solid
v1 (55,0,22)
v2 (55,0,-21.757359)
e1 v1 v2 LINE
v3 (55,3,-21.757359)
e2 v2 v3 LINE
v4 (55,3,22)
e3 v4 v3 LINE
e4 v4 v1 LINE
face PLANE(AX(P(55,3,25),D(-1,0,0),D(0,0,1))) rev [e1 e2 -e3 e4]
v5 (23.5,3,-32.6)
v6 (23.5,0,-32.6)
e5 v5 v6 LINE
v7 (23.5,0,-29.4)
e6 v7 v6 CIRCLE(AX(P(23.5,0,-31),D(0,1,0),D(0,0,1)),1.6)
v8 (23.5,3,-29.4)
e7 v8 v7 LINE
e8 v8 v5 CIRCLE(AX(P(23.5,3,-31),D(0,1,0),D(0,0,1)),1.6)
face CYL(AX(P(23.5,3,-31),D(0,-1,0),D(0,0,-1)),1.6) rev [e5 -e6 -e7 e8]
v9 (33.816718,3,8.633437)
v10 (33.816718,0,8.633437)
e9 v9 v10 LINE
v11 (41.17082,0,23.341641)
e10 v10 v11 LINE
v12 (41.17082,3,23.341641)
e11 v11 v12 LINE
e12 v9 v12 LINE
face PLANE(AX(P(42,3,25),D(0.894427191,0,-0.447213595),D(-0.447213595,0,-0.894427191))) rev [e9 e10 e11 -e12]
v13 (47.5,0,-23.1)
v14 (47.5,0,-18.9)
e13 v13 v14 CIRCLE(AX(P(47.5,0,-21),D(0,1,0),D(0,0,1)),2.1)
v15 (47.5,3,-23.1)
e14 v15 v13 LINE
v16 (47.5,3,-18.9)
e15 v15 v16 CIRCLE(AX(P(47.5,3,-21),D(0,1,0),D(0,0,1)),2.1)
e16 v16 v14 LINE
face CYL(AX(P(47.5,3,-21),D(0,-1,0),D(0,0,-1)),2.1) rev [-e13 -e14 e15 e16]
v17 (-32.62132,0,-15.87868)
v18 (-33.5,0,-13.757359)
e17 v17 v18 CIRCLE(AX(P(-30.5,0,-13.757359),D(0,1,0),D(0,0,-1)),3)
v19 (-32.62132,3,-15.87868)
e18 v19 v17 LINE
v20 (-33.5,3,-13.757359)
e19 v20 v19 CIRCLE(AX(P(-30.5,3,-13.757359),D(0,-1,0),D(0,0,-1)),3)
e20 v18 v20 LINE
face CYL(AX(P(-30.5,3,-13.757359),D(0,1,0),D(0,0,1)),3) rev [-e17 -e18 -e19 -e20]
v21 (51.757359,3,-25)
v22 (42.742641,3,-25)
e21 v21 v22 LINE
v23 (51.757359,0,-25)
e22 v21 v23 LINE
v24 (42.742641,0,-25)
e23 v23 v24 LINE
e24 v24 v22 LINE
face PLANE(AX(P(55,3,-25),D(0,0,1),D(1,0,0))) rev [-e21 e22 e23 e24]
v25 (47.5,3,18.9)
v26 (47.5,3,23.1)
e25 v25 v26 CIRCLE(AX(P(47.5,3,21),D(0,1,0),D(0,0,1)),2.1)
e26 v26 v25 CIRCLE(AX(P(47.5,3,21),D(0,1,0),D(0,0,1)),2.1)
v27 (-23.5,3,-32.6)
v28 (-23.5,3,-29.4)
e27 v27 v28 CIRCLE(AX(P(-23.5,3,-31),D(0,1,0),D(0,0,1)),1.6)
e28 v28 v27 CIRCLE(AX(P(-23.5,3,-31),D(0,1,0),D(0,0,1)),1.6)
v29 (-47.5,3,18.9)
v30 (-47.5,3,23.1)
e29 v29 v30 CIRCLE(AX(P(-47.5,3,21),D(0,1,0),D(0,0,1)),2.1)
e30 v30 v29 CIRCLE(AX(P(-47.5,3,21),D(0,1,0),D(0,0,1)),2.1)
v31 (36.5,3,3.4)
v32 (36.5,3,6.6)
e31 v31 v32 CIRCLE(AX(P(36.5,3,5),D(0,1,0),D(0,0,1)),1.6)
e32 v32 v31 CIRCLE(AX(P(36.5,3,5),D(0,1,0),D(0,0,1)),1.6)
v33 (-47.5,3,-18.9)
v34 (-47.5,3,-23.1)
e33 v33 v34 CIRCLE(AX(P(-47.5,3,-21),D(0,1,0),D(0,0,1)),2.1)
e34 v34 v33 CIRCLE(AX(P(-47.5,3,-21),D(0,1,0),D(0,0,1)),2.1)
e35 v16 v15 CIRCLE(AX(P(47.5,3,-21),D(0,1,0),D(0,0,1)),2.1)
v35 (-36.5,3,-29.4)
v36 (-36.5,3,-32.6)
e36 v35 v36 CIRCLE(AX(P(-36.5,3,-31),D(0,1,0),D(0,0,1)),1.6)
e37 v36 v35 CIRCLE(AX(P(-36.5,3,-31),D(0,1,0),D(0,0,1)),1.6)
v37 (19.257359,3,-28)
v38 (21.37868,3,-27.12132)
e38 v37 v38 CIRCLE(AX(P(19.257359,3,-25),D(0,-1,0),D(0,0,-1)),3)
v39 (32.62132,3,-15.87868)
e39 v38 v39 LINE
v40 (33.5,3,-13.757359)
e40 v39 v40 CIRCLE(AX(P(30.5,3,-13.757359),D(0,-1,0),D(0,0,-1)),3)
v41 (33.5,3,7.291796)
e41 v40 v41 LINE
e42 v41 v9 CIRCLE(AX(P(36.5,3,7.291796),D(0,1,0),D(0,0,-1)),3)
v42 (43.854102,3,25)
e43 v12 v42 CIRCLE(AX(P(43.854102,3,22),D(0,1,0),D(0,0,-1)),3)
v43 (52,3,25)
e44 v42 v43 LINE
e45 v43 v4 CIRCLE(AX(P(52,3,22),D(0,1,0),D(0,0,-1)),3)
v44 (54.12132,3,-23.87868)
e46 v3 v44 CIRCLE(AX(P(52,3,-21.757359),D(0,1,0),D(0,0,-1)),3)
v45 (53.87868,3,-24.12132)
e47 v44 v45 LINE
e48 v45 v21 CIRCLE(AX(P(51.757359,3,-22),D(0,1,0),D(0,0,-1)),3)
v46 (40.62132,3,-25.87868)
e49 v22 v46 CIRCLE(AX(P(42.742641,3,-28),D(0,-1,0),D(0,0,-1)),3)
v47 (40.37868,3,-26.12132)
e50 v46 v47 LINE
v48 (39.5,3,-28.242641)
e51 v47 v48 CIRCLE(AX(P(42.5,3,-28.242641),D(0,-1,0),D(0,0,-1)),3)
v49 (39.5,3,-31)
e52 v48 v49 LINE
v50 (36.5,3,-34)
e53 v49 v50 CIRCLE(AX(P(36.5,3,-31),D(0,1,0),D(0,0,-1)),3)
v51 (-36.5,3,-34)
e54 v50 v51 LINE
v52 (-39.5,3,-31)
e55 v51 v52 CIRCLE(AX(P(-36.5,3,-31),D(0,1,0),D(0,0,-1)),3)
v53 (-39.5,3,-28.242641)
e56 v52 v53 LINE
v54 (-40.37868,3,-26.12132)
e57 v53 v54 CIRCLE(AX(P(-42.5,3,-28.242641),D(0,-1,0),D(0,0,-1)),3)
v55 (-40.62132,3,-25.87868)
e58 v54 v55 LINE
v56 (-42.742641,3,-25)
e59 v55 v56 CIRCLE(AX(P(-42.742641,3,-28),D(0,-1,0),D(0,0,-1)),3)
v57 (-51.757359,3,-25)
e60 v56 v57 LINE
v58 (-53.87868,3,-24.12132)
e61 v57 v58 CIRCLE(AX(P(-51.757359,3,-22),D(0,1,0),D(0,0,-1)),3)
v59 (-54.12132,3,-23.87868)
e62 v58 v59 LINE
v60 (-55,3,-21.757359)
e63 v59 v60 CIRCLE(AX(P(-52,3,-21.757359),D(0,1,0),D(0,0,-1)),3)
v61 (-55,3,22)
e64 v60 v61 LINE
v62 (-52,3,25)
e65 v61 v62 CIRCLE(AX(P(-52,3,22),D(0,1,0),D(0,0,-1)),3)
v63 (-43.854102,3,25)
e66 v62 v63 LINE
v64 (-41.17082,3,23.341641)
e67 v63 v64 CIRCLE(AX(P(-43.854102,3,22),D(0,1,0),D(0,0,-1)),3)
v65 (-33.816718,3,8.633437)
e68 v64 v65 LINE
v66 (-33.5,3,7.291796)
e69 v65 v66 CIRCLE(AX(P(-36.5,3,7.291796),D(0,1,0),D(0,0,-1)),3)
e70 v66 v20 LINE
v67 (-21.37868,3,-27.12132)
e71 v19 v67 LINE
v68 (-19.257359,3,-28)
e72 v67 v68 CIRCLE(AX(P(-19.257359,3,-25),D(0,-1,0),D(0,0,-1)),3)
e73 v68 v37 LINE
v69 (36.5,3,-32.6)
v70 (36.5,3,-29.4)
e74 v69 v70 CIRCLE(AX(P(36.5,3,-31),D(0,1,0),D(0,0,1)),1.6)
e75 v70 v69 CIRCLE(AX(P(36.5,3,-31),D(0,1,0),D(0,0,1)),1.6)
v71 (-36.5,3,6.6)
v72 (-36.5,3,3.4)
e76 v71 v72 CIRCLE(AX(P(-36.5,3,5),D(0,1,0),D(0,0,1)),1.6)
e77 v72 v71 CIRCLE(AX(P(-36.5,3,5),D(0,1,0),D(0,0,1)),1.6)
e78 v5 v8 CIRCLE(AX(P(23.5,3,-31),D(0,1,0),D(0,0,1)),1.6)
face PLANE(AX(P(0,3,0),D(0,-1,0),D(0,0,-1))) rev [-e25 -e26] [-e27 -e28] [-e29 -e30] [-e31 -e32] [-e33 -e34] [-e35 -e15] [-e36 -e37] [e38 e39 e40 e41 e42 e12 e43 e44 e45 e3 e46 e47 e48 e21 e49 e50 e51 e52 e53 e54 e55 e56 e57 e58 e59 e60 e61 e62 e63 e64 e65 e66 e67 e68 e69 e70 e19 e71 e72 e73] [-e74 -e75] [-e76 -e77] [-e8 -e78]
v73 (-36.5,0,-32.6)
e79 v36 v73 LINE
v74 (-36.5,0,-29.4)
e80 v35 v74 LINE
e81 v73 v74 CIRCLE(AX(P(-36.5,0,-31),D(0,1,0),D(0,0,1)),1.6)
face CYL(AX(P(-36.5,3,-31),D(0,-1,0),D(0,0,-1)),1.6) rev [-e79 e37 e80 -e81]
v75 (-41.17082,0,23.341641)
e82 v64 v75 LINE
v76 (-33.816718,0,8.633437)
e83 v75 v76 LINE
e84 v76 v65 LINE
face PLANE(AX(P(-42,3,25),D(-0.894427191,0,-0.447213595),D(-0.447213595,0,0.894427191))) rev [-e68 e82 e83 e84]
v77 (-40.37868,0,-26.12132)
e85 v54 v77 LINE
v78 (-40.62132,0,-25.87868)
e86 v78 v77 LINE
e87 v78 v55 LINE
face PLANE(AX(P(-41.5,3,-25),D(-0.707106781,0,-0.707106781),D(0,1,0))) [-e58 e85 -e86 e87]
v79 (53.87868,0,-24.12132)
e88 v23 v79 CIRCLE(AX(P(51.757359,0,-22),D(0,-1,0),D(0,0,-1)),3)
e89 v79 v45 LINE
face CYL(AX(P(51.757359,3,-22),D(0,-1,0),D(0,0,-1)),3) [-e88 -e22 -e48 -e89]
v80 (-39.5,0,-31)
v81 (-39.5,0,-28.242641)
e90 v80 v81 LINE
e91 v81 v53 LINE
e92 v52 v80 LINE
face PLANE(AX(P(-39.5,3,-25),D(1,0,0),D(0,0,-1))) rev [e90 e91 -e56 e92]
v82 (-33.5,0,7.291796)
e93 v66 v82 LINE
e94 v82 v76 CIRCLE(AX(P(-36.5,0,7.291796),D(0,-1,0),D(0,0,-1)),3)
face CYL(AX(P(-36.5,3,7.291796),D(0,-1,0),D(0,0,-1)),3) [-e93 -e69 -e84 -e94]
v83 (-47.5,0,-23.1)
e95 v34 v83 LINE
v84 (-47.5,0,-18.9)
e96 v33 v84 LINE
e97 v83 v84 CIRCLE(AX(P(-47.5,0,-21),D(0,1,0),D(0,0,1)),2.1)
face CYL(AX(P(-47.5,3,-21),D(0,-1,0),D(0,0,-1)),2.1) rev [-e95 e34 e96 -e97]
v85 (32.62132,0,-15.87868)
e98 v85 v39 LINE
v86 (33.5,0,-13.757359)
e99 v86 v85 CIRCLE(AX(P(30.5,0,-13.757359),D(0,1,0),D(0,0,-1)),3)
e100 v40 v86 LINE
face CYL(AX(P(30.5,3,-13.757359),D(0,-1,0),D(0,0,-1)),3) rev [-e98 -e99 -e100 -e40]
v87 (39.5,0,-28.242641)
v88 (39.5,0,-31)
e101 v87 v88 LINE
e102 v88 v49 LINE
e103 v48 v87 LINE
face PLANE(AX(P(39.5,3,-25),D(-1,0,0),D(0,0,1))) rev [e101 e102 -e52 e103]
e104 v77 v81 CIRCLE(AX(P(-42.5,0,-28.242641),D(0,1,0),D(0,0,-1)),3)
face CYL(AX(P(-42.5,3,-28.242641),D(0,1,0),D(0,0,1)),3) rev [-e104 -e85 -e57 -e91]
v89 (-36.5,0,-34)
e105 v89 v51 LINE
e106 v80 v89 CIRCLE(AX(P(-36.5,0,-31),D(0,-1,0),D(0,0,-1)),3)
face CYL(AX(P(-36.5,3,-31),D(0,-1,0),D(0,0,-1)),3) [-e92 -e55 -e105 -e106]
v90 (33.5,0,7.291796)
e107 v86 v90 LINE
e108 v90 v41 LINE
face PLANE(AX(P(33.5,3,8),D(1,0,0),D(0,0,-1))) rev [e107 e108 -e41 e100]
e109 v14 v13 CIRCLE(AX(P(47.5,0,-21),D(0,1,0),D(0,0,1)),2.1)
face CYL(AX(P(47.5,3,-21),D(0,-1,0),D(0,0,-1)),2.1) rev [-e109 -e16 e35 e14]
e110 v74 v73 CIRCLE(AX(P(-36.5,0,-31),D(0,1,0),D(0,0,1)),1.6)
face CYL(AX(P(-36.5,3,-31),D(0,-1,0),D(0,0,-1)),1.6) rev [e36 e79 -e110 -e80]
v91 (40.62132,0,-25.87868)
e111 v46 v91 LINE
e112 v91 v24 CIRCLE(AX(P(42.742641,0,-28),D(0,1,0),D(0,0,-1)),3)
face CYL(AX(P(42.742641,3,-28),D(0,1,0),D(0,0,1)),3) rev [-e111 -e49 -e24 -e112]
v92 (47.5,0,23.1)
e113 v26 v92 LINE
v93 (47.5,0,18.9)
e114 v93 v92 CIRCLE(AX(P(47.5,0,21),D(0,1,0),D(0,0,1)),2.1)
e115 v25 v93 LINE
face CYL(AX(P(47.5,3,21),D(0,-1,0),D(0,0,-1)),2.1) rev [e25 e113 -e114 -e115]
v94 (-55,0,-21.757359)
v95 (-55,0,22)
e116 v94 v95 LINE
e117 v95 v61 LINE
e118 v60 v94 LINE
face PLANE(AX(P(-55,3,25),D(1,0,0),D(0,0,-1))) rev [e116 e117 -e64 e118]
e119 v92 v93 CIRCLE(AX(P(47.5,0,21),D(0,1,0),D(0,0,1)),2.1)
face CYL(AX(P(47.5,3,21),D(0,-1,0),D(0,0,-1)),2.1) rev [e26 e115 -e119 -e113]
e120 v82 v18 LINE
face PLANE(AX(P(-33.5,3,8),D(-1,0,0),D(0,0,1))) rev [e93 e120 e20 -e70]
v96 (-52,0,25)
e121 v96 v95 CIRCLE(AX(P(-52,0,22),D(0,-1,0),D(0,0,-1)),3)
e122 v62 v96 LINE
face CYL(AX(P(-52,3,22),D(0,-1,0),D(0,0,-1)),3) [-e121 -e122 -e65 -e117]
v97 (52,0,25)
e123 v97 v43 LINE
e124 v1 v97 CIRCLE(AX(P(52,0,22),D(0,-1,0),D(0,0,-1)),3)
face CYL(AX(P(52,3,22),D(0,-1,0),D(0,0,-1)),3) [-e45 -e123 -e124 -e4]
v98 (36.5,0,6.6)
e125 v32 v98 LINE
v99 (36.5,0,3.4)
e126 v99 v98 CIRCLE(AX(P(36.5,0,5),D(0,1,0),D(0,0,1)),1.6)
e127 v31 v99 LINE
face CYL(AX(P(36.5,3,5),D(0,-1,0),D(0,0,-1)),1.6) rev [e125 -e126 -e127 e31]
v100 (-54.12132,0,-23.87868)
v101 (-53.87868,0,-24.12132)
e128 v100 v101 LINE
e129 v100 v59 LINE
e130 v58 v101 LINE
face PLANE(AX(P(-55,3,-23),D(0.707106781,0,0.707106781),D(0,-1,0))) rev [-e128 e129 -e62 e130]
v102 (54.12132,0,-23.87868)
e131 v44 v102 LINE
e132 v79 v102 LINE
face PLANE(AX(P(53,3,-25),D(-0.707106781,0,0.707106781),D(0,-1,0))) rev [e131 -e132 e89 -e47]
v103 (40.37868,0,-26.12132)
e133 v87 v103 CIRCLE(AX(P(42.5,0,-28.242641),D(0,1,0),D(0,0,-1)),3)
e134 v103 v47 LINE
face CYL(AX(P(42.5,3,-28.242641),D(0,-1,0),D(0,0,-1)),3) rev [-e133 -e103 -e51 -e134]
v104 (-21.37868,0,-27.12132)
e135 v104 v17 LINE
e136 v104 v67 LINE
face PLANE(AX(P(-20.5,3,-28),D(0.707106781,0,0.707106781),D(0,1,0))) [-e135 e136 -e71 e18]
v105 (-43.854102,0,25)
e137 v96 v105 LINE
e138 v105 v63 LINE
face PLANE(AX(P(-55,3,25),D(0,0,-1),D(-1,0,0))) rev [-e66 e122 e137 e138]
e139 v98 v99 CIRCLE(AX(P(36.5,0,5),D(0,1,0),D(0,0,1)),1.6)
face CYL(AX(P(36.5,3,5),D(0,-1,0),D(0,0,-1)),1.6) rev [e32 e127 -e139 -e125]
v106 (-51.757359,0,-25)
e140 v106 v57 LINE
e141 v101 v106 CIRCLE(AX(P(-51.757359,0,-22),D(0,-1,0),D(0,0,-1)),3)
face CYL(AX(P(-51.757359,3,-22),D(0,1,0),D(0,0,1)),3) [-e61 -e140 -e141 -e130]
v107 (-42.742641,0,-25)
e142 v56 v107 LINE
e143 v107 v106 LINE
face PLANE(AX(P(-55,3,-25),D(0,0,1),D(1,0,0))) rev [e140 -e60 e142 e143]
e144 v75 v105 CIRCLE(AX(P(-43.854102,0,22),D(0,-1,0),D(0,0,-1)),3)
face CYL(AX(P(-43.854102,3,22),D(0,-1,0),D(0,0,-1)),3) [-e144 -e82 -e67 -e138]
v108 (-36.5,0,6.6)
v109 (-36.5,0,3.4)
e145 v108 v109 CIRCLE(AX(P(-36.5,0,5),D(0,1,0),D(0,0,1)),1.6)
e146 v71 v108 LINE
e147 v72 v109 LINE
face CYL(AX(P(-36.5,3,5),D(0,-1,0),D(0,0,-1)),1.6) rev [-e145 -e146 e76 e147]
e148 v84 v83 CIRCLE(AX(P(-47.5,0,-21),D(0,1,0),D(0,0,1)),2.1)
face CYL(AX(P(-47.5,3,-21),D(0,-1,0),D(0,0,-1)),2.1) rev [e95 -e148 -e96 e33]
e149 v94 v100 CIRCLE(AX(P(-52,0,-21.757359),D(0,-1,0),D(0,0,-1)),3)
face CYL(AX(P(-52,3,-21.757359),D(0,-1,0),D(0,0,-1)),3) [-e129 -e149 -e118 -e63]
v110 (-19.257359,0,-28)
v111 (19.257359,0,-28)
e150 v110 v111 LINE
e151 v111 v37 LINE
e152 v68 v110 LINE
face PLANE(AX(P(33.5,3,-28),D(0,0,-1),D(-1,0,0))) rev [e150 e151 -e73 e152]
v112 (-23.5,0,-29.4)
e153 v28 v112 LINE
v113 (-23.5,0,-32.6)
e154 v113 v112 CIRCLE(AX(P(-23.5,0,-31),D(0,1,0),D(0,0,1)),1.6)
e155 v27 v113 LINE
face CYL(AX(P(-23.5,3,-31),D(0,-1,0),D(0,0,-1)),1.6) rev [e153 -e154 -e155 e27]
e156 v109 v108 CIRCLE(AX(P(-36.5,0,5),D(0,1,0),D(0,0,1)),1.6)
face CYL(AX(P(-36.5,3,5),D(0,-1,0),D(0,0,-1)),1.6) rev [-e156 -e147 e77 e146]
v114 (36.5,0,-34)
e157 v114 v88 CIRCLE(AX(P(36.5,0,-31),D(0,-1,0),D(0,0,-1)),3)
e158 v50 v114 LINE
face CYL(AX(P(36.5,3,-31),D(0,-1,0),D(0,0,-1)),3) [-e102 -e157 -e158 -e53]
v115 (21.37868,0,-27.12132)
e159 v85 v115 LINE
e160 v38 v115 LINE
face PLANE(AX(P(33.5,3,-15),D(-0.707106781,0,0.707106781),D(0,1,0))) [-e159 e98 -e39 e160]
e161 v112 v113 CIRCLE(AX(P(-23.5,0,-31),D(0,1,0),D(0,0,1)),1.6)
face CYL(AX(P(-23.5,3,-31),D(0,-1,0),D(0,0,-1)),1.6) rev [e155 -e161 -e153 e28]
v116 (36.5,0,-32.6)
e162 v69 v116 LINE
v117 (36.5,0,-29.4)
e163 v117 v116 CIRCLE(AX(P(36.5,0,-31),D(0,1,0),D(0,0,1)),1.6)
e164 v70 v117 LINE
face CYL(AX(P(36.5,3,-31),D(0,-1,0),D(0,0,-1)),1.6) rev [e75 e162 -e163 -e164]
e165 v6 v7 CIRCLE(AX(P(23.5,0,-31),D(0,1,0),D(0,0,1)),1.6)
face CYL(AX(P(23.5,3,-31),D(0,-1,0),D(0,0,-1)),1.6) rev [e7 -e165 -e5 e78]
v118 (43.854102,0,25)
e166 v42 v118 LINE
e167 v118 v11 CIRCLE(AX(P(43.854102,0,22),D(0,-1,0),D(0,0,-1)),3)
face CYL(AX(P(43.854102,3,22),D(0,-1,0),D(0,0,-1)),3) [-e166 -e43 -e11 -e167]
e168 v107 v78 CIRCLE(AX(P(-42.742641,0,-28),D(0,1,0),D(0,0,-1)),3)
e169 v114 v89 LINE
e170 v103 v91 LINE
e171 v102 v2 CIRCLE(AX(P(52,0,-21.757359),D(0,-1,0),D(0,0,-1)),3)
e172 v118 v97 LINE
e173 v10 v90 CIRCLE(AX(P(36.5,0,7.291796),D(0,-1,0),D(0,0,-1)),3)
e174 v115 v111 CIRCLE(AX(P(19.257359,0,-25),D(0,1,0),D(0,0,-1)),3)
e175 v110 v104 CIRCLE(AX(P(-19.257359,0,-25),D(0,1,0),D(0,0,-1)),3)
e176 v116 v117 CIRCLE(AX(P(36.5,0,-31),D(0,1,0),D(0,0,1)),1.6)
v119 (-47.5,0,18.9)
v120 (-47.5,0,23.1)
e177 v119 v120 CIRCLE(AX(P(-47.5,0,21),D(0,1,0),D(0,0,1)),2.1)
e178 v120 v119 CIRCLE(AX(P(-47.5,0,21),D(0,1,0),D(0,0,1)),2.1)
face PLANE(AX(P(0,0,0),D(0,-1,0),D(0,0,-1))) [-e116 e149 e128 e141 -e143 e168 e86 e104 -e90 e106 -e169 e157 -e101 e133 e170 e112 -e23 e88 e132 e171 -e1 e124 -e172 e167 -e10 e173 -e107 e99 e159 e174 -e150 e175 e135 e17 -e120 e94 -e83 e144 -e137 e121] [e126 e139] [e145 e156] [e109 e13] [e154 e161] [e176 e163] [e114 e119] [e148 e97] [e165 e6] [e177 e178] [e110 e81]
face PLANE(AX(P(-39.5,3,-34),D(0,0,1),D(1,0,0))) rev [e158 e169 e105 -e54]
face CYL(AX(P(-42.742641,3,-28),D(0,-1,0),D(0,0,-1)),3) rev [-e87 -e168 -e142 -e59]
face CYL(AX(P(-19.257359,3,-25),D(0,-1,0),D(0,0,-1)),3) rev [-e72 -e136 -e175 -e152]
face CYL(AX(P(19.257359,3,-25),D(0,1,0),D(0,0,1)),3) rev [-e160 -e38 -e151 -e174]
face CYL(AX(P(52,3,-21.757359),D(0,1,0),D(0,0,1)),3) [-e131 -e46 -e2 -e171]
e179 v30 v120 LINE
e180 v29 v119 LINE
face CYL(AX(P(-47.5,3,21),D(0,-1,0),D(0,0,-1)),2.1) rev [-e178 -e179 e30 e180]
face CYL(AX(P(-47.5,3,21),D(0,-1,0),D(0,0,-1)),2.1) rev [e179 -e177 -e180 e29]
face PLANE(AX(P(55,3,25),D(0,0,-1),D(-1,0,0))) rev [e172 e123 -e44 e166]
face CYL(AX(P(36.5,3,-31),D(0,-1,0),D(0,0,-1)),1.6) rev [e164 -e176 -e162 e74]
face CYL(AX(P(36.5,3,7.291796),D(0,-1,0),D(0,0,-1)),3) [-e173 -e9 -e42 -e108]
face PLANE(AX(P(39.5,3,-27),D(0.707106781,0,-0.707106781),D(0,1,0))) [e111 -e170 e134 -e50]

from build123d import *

# Parameters (mm, degrees)
SKETCH_1_R      = 2.1
SKETCH_1_R_2    = 1.6
EXTRUDE_1_DEPTH = 3
CHAMFER_1_SIZE  = 13
CHAMFER_2_SIZE  = 2
FILLET_1_R      = 3


with BuildPart() as part:
    # 草图1 → 凸台-拉伸1 (new body)
    with BuildSketch(Plane(origin=(0, 0, 0), x_dir=(1, 0, 0), z_dir=(0, 1, 0))):
        Polygon((-55, -25), (-55, 25), (-39.5, 25), (-39.5, 34), (39.5, 34), (39.5, 25), (55, 25), (55, -25), (42, -25), (33.5, -8), (33.5, 28), (0, 28), (-33.5, 28), (-33.5, -8), (-42, -25), align=None)
        with Locations(Location((-47.5, 21, 0), (0, 0, 270))):
            Circle(SKETCH_1_R, mode=Mode.SUBTRACT)
        with Locations(Location((-47.5, -21, 0), (0, 0, 270))):
            Circle(SKETCH_1_R, mode=Mode.SUBTRACT)
        with Locations(Location((47.5, -21, 0), (0, 0, 270))):
            Circle(SKETCH_1_R, mode=Mode.SUBTRACT)
        with Locations(Location((47.5, 21, 0), (0, 0, 270))):
            Circle(SKETCH_1_R, mode=Mode.SUBTRACT)
        with Locations(Location((-36.5, 31, 0), (0, 0, 270))):
            Circle(SKETCH_1_R_2, mode=Mode.SUBTRACT)
        with Locations(Location((-36.5, -5, 0), (0, 0, 270))):
            Circle(SKETCH_1_R_2, mode=Mode.SUBTRACT)
        with Locations(Location((36.5, -5, 0), (0, 0, 270))):
            Circle(SKETCH_1_R_2, mode=Mode.SUBTRACT)
        with Locations(Location((36.5, 31, 0), (0, 0, 270))):
            Circle(SKETCH_1_R_2, mode=Mode.SUBTRACT)
        with Locations(Location((-23.5, 31, 0), (0, 0, 270))):
            Circle(SKETCH_1_R_2, mode=Mode.SUBTRACT)
        with Locations(Location((23.5, 31, 0), (0, 0, 270))):
            Circle(SKETCH_1_R_2, mode=Mode.SUBTRACT)
    extrude(amount=EXTRUDE_1_DEPTH)

    # 倒角1
    chamfer_1_edges = [part.edges().sort_by_distance(p)[0] for p in [
        (33.5, 1.5, -28),
        (-33.5, 1.5, -28),
    ]]
    chamfer(chamfer_1_edges, length=CHAMFER_1_SIZE)

    # 倒角2
    chamfer_2_edges = [part.edges().sort_by_distance(p)[0] for p in [
        (55, 1.5, -25),
        (-55, 1.5, -25),
        (-39.5, 1.5, -25),
        (39.5, 1.5, -25),
    ]]
    chamfer(chamfer_2_edges, length=CHAMFER_2_SIZE)

    # 圆角1
    fillet_1_edges = [part.edges().sort_by_distance(p)[0] for p in [
        (41.5, 1.5, -25),
        (53, 1.5, -25),
        (55, 1.5, -23),
        (39.5, 1.5, -27),
        (-55, 1.5, -23),
        (-41.5, 1.5, -25),
        (-53, 1.5, -25),
        (-39.5, 1.5, -27),
        (55, 1.5, 25),
        (42, 1.5, 25),
        (33.5, 1.5, 8),
        (-33.5, 1.5, 8),
        (-42, 1.5, 25),
        (-55, 1.5, 25),
        (-39.5, 1.5, -34),
        (39.5, 1.5, -34),
        (33.5, 1.5, -15),
        (-20.5, 1.5, -28),
        (20.5, 1.5, -28),
        (-33.5, 1.5, -15),
    ]]
    fillet(fillet_1_edges, radius=FILLET_1_R)


solid = part.part
